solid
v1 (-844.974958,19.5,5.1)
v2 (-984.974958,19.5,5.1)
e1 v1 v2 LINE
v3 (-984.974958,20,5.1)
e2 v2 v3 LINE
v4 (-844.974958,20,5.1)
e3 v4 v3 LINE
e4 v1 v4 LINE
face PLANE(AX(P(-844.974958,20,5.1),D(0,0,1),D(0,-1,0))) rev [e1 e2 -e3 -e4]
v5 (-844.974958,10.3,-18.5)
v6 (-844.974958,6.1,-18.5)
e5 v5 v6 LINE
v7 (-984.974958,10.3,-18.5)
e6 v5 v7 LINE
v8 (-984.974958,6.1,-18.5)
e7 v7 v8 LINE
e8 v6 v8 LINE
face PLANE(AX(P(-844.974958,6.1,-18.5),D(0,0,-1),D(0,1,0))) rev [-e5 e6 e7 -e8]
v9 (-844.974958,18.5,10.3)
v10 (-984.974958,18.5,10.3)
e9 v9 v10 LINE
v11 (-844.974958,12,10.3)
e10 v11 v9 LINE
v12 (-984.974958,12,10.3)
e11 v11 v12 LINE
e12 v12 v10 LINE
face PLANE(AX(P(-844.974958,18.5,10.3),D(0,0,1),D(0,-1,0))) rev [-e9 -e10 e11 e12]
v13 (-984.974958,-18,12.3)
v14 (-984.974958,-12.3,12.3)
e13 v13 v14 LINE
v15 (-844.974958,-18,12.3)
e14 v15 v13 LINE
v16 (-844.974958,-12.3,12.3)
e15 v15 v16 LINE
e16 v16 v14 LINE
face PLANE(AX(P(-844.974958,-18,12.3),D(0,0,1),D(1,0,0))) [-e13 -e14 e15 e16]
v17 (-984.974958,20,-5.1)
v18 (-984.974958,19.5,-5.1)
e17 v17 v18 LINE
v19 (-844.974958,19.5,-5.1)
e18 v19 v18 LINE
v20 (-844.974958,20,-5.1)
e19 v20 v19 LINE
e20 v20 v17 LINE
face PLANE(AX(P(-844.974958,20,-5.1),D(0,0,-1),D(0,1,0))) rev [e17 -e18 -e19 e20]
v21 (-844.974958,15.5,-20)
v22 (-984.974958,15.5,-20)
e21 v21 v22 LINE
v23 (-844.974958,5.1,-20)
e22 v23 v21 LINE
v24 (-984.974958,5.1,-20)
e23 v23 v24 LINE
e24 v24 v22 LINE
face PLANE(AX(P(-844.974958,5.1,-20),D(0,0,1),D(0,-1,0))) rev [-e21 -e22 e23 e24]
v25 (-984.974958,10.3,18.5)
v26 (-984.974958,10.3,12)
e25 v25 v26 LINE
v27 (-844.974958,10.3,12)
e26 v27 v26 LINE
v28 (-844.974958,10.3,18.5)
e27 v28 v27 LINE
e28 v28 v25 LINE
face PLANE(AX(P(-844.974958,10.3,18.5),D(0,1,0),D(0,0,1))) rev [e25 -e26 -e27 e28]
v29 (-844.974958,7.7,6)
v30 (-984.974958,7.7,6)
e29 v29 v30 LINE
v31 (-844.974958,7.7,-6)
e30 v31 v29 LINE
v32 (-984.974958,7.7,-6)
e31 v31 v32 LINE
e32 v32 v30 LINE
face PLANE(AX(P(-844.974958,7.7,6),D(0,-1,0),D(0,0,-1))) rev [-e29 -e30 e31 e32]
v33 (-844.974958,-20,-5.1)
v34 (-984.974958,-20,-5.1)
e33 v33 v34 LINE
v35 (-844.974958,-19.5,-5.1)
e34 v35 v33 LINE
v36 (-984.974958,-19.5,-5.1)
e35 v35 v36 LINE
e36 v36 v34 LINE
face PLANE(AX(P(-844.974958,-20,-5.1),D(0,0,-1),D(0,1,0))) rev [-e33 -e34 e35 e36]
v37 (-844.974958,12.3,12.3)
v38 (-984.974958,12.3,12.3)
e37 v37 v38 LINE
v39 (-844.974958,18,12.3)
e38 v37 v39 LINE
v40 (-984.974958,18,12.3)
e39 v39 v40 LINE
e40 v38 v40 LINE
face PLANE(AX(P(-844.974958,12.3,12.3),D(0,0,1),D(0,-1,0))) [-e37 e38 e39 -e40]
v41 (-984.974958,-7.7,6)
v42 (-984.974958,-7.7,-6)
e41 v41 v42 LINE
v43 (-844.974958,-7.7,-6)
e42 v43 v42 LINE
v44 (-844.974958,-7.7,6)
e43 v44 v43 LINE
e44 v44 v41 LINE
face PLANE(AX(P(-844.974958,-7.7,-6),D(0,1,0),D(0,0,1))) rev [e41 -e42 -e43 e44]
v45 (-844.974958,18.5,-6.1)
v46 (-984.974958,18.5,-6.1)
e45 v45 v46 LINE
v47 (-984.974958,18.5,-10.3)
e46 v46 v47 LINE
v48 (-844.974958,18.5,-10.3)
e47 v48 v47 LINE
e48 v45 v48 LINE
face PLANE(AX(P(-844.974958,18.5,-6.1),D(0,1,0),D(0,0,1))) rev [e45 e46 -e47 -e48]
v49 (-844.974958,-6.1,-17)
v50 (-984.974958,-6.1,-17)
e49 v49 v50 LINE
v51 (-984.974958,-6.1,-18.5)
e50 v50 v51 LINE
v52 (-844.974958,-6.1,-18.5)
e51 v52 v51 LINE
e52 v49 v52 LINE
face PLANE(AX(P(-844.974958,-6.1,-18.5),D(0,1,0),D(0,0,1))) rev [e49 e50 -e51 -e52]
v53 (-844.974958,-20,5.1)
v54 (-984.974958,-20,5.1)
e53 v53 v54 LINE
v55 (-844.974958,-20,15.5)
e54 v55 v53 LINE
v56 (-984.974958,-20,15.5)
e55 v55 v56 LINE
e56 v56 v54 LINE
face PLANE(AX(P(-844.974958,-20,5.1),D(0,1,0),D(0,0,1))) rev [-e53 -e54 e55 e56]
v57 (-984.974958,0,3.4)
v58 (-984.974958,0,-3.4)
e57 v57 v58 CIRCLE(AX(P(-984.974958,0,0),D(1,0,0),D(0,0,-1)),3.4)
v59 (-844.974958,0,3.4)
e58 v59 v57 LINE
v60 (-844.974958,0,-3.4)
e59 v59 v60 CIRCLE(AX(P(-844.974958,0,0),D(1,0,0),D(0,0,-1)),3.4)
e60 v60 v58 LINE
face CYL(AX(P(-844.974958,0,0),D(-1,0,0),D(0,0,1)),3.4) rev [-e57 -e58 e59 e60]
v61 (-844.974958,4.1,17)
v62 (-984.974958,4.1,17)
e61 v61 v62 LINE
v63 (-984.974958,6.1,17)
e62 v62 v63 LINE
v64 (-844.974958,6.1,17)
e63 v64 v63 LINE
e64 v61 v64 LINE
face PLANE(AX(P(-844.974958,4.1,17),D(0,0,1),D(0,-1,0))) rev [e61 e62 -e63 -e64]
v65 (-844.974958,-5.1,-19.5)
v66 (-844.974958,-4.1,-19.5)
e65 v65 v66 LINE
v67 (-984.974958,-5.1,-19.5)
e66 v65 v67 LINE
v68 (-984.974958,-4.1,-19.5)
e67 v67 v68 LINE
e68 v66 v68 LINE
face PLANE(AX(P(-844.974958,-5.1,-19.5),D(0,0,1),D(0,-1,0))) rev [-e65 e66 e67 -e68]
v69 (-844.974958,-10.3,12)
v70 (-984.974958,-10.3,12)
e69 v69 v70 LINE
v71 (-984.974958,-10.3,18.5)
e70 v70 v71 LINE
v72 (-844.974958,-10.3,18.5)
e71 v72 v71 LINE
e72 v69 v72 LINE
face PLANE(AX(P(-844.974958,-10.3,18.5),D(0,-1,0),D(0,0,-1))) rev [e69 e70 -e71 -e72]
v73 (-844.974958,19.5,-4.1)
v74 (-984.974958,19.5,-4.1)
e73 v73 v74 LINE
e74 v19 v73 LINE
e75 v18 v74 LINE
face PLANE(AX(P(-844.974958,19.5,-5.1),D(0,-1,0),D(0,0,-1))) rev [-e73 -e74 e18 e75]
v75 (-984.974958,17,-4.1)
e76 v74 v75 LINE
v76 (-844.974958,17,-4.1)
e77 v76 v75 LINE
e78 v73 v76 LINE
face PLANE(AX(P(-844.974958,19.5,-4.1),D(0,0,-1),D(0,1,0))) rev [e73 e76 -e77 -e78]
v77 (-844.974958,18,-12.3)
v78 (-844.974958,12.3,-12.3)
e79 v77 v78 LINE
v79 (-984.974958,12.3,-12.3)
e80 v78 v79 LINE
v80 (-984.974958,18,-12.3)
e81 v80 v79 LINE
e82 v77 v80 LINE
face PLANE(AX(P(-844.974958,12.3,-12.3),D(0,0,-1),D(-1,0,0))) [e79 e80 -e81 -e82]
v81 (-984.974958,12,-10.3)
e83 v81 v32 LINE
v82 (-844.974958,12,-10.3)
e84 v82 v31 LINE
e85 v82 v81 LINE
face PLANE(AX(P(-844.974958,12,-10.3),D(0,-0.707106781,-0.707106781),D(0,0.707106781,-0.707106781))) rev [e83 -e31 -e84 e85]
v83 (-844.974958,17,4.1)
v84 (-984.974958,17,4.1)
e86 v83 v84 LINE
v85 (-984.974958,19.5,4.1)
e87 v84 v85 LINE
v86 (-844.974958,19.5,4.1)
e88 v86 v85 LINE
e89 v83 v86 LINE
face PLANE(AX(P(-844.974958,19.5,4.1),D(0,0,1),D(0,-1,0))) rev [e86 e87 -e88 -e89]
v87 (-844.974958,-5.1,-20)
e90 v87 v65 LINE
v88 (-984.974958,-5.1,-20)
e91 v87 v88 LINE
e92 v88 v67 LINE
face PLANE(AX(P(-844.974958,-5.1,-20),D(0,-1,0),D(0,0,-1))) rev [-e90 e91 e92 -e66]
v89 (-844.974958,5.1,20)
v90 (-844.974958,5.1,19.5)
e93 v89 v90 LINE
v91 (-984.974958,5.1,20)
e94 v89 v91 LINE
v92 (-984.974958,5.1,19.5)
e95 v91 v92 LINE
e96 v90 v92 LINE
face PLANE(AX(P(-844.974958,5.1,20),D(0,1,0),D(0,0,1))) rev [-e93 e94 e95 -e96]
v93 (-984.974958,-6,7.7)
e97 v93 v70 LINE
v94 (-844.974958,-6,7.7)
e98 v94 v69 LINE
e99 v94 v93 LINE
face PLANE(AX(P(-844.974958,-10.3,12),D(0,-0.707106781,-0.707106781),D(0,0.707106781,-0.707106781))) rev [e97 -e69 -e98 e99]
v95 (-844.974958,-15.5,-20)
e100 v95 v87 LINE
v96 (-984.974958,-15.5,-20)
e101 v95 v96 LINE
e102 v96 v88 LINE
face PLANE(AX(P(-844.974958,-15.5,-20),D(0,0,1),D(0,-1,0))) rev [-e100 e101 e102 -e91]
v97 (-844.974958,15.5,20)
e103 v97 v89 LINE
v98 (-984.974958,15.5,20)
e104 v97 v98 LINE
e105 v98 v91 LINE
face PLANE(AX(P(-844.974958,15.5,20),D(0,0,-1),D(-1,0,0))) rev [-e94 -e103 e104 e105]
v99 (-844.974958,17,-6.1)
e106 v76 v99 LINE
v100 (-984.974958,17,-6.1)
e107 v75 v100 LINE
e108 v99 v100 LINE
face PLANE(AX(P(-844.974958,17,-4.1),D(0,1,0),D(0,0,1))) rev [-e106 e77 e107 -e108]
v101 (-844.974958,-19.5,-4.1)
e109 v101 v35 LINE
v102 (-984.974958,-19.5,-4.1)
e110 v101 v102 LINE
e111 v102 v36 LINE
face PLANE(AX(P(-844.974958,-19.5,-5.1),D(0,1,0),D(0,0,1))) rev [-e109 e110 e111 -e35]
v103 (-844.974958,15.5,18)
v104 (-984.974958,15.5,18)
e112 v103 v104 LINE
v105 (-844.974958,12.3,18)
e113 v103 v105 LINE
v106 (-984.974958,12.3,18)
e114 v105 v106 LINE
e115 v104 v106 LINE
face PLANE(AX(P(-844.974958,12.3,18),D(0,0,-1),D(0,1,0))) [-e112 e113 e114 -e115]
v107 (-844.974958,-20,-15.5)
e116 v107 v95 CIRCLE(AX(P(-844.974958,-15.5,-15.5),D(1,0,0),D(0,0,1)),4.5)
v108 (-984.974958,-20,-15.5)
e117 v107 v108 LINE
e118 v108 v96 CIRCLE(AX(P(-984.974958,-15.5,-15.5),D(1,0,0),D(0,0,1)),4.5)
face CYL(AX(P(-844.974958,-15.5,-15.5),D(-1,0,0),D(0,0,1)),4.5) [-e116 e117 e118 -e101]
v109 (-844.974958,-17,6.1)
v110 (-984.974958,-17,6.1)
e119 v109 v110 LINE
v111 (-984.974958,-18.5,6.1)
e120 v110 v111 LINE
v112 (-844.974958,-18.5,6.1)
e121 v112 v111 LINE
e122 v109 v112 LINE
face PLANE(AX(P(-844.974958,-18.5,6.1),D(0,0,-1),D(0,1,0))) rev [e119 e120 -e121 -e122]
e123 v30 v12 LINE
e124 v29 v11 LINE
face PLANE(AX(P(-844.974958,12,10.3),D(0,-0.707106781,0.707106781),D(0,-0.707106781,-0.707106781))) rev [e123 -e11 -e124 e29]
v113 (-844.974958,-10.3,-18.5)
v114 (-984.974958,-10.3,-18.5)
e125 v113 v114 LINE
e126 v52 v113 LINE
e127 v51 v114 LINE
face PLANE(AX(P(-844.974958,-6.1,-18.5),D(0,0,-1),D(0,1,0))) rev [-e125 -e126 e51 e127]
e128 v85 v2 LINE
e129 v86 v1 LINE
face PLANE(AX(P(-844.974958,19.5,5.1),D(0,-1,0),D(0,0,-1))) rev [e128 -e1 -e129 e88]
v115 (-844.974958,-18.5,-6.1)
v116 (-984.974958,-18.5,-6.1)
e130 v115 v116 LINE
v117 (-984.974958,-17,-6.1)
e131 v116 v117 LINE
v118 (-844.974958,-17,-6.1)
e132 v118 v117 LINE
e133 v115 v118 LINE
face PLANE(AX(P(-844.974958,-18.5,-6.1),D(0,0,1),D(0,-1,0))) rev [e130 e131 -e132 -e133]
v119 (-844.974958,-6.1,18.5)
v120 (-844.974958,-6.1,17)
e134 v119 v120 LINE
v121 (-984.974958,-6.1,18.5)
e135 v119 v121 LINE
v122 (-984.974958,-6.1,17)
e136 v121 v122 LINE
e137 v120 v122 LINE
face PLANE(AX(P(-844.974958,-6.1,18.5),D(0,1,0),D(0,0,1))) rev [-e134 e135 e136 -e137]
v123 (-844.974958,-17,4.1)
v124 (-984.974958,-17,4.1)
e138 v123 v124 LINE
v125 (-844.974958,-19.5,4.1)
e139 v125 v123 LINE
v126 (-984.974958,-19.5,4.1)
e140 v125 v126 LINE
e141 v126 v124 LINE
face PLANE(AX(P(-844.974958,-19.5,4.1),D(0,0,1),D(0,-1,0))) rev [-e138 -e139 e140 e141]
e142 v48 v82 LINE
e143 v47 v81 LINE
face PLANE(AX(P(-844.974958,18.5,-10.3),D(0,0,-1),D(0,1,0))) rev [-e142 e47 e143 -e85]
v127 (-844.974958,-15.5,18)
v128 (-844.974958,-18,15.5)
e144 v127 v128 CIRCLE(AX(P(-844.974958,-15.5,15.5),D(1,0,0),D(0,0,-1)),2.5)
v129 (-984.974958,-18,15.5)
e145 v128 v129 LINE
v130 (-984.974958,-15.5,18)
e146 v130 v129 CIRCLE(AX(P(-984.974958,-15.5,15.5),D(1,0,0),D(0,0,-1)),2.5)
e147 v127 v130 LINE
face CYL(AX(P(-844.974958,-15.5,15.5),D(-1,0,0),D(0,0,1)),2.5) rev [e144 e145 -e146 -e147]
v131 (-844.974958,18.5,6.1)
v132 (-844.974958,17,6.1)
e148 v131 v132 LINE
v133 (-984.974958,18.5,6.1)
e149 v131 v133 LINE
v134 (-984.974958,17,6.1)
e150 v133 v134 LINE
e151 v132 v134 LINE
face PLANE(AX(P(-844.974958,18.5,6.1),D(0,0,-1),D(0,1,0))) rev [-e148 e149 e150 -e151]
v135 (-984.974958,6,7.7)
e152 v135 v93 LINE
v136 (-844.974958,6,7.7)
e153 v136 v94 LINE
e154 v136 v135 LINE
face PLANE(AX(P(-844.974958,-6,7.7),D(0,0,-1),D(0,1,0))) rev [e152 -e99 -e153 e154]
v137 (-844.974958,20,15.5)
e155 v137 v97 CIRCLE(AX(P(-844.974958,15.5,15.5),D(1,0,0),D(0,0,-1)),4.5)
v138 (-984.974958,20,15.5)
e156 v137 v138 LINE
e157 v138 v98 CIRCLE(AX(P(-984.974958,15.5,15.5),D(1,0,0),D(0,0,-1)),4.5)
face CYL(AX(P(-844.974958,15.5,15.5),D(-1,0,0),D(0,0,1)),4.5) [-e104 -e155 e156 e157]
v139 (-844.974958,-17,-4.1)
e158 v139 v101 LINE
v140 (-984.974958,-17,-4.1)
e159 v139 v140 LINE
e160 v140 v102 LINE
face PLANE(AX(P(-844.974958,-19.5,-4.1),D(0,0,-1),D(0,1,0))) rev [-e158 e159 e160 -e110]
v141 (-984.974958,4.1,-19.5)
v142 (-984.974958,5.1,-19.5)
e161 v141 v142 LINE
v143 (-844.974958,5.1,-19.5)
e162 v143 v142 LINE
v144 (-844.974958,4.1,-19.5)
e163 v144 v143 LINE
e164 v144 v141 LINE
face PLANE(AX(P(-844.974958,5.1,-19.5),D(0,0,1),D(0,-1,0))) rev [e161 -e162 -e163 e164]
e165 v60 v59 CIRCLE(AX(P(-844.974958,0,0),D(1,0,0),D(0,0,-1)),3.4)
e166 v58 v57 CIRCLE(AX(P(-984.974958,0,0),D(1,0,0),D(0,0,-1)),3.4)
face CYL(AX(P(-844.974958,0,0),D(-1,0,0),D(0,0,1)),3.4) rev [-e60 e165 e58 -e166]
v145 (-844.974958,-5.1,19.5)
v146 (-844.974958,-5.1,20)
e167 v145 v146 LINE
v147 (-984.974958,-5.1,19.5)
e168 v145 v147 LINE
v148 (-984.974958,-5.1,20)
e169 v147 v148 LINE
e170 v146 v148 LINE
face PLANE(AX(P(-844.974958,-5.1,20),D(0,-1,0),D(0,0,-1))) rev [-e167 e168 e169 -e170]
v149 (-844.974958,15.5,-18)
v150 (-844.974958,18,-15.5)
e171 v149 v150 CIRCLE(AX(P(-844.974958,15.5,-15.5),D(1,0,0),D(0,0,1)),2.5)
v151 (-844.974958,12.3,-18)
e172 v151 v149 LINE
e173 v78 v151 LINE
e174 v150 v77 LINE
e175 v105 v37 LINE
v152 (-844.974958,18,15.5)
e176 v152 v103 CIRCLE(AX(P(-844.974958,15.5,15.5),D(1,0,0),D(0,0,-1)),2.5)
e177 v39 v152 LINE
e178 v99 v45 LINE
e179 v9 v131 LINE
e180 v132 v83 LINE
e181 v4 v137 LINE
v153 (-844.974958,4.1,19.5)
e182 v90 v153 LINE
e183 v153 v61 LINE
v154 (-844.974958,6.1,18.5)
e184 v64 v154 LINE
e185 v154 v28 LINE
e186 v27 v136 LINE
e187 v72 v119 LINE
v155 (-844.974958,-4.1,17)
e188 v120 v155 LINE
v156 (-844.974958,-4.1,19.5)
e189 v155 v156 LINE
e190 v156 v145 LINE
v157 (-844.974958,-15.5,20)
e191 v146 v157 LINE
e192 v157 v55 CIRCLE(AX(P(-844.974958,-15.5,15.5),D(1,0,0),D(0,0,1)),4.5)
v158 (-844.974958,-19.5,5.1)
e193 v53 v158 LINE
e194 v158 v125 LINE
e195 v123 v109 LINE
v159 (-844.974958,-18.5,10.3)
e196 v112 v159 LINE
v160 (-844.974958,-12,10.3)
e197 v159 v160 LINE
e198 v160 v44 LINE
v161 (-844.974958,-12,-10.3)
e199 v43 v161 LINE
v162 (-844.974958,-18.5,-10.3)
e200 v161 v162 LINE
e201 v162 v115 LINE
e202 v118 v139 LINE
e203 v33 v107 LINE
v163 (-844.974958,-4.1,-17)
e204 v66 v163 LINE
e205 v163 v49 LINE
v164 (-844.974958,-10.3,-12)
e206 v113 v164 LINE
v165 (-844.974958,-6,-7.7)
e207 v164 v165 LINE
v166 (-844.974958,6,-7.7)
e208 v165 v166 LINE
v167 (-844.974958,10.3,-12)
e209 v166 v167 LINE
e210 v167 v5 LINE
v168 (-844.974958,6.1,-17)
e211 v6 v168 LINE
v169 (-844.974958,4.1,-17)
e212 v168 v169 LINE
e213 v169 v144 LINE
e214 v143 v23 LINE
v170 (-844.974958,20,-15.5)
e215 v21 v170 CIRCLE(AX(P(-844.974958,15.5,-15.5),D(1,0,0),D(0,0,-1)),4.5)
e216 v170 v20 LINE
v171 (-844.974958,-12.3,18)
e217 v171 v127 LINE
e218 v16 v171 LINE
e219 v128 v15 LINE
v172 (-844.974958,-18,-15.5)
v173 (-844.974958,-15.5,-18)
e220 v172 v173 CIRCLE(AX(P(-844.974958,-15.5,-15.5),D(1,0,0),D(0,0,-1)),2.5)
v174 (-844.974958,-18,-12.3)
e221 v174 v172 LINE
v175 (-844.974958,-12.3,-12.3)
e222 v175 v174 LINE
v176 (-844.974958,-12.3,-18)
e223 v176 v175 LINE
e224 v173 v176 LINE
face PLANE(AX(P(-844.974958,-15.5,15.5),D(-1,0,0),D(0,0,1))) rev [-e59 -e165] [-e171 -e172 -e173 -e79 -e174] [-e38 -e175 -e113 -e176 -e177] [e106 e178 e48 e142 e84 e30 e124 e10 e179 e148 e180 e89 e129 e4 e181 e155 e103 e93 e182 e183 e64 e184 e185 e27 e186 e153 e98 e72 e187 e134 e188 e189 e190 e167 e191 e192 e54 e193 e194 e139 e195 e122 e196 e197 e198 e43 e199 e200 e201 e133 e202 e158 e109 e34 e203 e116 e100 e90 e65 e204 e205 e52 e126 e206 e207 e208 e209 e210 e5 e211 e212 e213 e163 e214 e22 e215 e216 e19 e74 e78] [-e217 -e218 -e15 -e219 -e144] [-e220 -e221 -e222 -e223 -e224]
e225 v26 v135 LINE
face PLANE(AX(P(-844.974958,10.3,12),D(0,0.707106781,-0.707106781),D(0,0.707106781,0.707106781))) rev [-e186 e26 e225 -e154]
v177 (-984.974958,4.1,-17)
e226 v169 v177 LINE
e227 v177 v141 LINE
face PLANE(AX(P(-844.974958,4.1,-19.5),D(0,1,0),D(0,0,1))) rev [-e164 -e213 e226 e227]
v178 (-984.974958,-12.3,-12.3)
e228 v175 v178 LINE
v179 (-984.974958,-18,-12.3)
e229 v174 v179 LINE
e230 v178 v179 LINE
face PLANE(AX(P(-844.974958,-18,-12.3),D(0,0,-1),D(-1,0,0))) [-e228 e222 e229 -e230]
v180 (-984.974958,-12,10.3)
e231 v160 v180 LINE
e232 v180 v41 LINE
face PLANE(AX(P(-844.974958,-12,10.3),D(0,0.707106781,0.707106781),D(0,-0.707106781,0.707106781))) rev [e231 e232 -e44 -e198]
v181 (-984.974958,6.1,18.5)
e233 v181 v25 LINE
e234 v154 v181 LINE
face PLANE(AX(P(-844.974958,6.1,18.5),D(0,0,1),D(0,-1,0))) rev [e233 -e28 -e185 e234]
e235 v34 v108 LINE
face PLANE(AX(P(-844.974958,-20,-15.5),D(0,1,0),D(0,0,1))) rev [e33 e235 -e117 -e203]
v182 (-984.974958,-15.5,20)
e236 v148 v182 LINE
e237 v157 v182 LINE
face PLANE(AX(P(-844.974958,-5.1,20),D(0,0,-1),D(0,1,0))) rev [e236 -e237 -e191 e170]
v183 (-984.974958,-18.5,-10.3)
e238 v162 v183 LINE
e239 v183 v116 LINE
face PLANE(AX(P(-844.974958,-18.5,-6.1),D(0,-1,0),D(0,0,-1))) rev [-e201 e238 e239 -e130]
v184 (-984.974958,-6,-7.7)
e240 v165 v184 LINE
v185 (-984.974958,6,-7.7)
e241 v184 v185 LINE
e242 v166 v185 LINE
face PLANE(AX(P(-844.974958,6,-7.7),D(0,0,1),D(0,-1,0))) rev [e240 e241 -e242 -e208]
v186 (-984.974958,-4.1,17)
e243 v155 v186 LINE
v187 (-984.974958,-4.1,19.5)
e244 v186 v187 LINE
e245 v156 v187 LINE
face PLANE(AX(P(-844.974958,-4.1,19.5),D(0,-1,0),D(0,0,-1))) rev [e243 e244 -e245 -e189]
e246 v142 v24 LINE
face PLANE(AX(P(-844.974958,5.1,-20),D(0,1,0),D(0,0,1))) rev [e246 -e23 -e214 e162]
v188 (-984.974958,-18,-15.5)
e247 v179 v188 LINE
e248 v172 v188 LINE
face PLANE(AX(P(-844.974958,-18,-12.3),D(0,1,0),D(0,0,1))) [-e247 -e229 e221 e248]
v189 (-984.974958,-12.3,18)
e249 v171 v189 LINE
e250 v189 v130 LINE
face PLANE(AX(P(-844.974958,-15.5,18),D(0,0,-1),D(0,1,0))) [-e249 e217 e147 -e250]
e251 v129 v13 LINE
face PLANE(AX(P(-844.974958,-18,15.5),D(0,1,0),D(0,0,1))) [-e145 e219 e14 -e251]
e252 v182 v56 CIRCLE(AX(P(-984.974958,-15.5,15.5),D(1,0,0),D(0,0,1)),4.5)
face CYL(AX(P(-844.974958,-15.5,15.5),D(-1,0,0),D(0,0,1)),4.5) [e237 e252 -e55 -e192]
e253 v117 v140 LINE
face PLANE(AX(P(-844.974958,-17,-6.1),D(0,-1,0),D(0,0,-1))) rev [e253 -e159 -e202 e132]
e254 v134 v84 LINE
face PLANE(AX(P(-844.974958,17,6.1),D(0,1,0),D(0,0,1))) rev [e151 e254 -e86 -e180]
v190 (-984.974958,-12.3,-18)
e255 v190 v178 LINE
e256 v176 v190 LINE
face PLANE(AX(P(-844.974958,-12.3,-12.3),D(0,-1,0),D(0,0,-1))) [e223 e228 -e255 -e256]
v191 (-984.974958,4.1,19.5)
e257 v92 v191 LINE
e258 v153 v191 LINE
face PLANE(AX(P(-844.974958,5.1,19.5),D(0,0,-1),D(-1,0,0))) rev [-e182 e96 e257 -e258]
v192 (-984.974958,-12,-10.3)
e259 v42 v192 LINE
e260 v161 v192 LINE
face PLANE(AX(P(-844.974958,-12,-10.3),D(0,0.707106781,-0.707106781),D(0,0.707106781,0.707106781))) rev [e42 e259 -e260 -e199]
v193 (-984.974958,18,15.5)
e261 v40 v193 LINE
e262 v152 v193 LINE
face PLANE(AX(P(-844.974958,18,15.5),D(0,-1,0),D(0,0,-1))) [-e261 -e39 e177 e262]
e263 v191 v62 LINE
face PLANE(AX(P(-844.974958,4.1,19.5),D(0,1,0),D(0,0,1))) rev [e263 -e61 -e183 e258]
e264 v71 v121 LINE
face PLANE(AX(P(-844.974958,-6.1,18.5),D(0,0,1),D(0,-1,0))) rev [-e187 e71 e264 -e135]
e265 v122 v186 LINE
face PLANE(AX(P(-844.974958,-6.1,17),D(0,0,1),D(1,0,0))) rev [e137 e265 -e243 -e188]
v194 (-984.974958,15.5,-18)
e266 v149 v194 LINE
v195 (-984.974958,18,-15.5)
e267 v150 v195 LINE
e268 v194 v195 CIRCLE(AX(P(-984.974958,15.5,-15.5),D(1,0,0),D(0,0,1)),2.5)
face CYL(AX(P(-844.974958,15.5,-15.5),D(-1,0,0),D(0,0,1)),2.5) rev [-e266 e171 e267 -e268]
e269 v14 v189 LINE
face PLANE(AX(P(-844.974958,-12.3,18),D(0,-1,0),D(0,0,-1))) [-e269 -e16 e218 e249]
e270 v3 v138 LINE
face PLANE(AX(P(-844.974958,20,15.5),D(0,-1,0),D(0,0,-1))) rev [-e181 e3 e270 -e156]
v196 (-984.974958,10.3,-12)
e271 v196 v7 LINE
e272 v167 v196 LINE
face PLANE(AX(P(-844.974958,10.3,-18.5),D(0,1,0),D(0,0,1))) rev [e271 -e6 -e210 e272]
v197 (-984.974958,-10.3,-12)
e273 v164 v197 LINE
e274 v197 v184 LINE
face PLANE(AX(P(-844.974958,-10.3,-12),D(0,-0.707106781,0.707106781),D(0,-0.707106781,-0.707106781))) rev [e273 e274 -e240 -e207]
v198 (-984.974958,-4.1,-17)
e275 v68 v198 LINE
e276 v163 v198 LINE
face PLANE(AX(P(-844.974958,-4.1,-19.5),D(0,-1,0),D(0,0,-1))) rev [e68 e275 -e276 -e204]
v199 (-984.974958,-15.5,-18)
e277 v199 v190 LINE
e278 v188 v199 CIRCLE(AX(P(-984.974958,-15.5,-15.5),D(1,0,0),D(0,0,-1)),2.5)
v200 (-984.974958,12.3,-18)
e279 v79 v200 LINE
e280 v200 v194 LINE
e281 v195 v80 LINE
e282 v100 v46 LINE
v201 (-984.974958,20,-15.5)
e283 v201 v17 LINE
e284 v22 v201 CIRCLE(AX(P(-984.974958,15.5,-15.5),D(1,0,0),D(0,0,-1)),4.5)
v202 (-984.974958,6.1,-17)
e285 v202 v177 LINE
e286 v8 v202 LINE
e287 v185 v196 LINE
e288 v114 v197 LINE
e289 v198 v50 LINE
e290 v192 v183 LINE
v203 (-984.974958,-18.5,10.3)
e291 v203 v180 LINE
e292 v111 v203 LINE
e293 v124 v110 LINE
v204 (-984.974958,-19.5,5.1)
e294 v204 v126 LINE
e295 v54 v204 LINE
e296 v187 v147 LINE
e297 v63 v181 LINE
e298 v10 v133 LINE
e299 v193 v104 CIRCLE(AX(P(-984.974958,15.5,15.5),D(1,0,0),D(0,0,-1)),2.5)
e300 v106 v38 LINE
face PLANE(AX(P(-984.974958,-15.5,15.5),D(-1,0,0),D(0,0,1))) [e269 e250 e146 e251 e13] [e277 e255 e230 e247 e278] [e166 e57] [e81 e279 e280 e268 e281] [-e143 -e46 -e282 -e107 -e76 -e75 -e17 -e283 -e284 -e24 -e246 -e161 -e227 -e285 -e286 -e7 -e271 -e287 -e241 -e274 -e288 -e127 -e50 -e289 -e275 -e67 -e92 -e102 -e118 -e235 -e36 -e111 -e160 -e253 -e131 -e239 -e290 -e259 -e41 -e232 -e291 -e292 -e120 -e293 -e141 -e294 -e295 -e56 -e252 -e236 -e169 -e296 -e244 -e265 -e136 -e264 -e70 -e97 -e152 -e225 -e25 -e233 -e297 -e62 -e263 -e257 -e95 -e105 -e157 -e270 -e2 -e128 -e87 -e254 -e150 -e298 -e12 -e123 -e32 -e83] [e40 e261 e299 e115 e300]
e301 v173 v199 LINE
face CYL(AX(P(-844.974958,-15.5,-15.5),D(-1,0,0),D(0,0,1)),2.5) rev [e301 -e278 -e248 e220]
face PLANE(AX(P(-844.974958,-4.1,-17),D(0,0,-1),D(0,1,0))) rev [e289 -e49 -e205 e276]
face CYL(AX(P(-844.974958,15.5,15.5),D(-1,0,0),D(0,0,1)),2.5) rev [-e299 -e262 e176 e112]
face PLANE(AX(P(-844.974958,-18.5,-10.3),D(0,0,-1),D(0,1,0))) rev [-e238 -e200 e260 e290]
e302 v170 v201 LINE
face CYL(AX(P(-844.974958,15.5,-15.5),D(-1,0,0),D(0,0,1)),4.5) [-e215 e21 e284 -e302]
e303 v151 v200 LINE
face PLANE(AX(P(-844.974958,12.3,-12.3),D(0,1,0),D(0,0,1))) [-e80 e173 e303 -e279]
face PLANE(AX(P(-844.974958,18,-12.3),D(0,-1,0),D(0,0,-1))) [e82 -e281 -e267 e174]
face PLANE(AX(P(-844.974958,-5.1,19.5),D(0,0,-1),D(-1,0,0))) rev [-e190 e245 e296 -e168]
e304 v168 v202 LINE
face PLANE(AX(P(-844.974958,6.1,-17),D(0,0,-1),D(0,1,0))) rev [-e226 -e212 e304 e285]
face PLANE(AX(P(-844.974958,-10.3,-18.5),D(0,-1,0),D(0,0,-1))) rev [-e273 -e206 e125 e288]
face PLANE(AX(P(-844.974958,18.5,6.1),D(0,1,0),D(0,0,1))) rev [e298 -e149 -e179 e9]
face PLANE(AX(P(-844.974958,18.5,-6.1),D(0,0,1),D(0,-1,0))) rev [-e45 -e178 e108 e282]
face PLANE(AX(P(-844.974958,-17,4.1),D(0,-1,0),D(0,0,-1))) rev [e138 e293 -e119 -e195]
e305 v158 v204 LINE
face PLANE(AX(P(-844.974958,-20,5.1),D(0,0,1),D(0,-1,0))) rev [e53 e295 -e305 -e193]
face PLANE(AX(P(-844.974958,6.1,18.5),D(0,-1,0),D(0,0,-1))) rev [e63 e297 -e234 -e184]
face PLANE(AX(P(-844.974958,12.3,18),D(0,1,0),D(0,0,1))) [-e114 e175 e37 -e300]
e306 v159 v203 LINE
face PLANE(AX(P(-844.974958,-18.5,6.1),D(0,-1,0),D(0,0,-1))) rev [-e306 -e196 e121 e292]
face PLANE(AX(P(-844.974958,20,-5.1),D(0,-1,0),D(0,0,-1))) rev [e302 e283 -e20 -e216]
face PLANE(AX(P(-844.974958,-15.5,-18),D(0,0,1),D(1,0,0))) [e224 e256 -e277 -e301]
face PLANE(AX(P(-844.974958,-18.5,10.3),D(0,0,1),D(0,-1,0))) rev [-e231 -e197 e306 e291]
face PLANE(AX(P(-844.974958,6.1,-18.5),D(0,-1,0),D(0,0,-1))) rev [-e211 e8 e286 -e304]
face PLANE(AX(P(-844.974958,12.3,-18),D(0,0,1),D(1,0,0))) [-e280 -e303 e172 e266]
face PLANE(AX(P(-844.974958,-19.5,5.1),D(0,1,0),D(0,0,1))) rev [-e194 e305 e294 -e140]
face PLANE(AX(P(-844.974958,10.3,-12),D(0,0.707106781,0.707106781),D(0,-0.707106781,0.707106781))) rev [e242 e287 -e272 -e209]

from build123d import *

# Parameters (mm, degrees)
SKETCH1_R                                 = 3.4
ALUMINIUM_PROFILE_40_X_40B_X_R4_5_1_DEPTH = 140


with BuildPart() as part:
    # Sketch1 → Aluminium profile 40 X 40B X R4.5(1) (new body)
    with BuildSketch(Plane.YZ.offset(-984.974958264)):
        with BuildLine():
            Line((-5.1, 20), (-5.1, 19.5))
            Line((-5.1, 19.5), (-4.1, 19.5))
            Line((-4.1, 19.5), (-4.1, 17))
            Line((-4.1, 17), (-6.1, 17))
            Line((-6.1, 17), (-6.1, 18.5))
            Line((-6.1, 18.5), (-10.3, 18.5))
            Line((-10.3, 18.5), (-10.3, 12))
            Line((-10.3, 12), (-6, 7.7))
            Line((-6, 7.7), (6, 7.7))
            Line((6, 7.7), (10.3, 12))
            Line((10.3, 12), (10.3, 18.5))
            Line((10.3, 18.5), (6.1, 18.5))
            Line((6.1, 18.5), (6.1, 17))
            Line((6.1, 17), (4.1, 17))
            Line((4.1, 17), (4.1, 19.5))
            Line((4.1, 19.5), (5.1, 19.5))
            Line((5.1, 19.5), (5.1, 20))
            Line((5.1, 20), (15.5, 20))
            ThreePointArc((15.5, 20), (18.681980515, 18.681980515), (20, 15.5))
            Line((20, 15.5), (20, 5.1))
            Line((20, 5.1), (19.5, 5.1))
            Line((19.5, 5.1), (19.5, 4.1))
            Line((19.5, 4.1), (17, 4.1))
            Line((17, 4.1), (17, 6.1))
            Line((17, 6.1), (18.5, 6.1))
            Line((18.5, 6.1), (18.5, 10.3))
            Line((18.5, 10.3), (12, 10.3))
            Line((12, 10.3), (7.7, 6))
            Line((7.7, 6), (7.7, -6))
            Line((7.7, -6), (12, -10.3))
            Line((12, -10.3), (18.5, -10.3))
            Line((18.5, -10.3), (18.5, -6.1))
            Line((18.5, -6.1), (17, -6.1))
            Line((17, -6.1), (17, -4.1))
            Line((17, -4.1), (19.5, -4.1))
            Line((19.5, -4.1), (19.5, -5.1))
            Line((19.5, -5.1), (20, -5.1))
            Line((20, -5.1), (20, -15.5))
            ThreePointArc((20, -15.5), (18.681980515, -18.681980515), (15.5, -20))
            Line((15.5, -20), (5.1, -20))
            Line((5.1, -20), (5.1, -19.5))
            Line((5.1, -19.5), (4.1, -19.5))
            Line((4.1, -19.5), (4.1, -17))
            Line((4.1, -17), (6.1, -17))
            Line((6.1, -17), (6.1, -18.5))
            Line((6.1, -18.5), (10.3, -18.5))
            Line((10.3, -18.5), (10.3, -12))
            Line((10.3, -12), (6, -7.7))
            Line((6, -7.7), (-6, -7.7))
            Line((-6, -7.7), (-10.3, -12))
            Line((-10.3, -12), (-10.3, -18.5))
            Line((-10.3, -18.5), (-6.1, -18.5))
            Line((-6.1, -18.5), (-6.1, -17))
            Line((-6.1, -17), (-4.1, -17))
            Line((-4.1, -17), (-4.1, -19.5))
            Line((-4.1, -19.5), (-5.1, -19.5))
            Line((-5.1, -19.5), (-5.1, -20))
            Line((-5.1, -20), (-15.5, -20))
            ThreePointArc((-15.5, -20), (-18.681980515, -18.681980515), (-20, -15.5))
            Line((-20, -15.5), (-20, -5.1))
            Line((-20, -5.1), (-19.5, -5.1))
            Line((-19.5, -5.1), (-19.5, -4.1))
            Line((-19.5, -4.1), (-17, -4.1))
            Line((-17, -4.1), (-17, -6.1))
            Line((-17, -6.1), (-18.5, -6.1))
            Line((-18.5, -6.1), (-18.5, -10.3))
            Line((-18.5, -10.3), (-12, -10.3))
            Line((-12, -10.3), (-7.7, -6))
            Line((-7.7, -6), (-7.7, 6))
            Line((-7.7, 6), (-12, 10.3))
            Line((-12, 10.3), (-18.5, 10.3))
            Line((-18.5, 10.3), (-18.5, 6.1))
            Line((-18.5, 6.1), (-17, 6.1))
            Line((-17, 6.1), (-17, 4.1))
            Line((-17, 4.1), (-19.5, 4.1))
            Line((-19.5, 4.1), (-19.5, 5.1))
            Line((-19.5, 5.1), (-20, 5.1))
            Line((-20, 5.1), (-20, 15.5))
            ThreePointArc((-20, 15.5), (-18.681980515, 18.681980515), (-15.5, 20))
            Line((-15.5, 20), (-5.1, 20))
        make_face()
        Circle(SKETCH1_R, mode=Mode.SUBTRACT)
        with BuildLine():
            Line((12.3, 18), (15.5, 18))
            ThreePointArc((15.5, 18), (17.267766953, 17.267766953), (18, 15.5))
            Line((18, 15.5), (18, 12.3))
            Line((18, 12.3), (12.3, 12.3))
            Line((12.3, 12.3), (12.3, 18))
        make_face(mode=Mode.SUBTRACT)
        with BuildLine():
            Line((-15.5, 18), (-12.3, 18))
            Line((-12.3, 18), (-12.3, 12.3))
            Line((-12.3, 12.3), (-18, 12.3))
            Line((-18, 12.3), (-18, 15.5))
            ThreePointArc((-18, 15.5), (-17.267766953, 17.267766953), (-15.5, 18))
        make_face(mode=Mode.SUBTRACT)
        with BuildLine():
            Line((-18, -12.3), (-12.3, -12.3))
            Line((-12.3, -12.3), (-12.3, -18))
            Line((-12.3, -18), (-15.5, -18))
            ThreePointArc((-15.5, -18), (-17.267766953, -17.267766953), (-18, -15.5))
            Line((-18, -15.5), (-18, -12.3))
        make_face(mode=Mode.SUBTRACT)
        with BuildLine():
            Line((12.3, -12.3), (18, -12.3))
            Line((18, -12.3), (18, -15.5))
            ThreePointArc((18, -15.5), (17.267766953, -17.267766953), (15.5, -18))
            Line((15.5, -18), (12.3, -18))
            Line((12.3, -18), (12.3, -12.3))
        make_face(mode=Mode.SUBTRACT)
    extrude(amount=ALUMINIUM_PROFILE_40_X_40B_X_R4_5_1_DEPTH)


solid = part.part
